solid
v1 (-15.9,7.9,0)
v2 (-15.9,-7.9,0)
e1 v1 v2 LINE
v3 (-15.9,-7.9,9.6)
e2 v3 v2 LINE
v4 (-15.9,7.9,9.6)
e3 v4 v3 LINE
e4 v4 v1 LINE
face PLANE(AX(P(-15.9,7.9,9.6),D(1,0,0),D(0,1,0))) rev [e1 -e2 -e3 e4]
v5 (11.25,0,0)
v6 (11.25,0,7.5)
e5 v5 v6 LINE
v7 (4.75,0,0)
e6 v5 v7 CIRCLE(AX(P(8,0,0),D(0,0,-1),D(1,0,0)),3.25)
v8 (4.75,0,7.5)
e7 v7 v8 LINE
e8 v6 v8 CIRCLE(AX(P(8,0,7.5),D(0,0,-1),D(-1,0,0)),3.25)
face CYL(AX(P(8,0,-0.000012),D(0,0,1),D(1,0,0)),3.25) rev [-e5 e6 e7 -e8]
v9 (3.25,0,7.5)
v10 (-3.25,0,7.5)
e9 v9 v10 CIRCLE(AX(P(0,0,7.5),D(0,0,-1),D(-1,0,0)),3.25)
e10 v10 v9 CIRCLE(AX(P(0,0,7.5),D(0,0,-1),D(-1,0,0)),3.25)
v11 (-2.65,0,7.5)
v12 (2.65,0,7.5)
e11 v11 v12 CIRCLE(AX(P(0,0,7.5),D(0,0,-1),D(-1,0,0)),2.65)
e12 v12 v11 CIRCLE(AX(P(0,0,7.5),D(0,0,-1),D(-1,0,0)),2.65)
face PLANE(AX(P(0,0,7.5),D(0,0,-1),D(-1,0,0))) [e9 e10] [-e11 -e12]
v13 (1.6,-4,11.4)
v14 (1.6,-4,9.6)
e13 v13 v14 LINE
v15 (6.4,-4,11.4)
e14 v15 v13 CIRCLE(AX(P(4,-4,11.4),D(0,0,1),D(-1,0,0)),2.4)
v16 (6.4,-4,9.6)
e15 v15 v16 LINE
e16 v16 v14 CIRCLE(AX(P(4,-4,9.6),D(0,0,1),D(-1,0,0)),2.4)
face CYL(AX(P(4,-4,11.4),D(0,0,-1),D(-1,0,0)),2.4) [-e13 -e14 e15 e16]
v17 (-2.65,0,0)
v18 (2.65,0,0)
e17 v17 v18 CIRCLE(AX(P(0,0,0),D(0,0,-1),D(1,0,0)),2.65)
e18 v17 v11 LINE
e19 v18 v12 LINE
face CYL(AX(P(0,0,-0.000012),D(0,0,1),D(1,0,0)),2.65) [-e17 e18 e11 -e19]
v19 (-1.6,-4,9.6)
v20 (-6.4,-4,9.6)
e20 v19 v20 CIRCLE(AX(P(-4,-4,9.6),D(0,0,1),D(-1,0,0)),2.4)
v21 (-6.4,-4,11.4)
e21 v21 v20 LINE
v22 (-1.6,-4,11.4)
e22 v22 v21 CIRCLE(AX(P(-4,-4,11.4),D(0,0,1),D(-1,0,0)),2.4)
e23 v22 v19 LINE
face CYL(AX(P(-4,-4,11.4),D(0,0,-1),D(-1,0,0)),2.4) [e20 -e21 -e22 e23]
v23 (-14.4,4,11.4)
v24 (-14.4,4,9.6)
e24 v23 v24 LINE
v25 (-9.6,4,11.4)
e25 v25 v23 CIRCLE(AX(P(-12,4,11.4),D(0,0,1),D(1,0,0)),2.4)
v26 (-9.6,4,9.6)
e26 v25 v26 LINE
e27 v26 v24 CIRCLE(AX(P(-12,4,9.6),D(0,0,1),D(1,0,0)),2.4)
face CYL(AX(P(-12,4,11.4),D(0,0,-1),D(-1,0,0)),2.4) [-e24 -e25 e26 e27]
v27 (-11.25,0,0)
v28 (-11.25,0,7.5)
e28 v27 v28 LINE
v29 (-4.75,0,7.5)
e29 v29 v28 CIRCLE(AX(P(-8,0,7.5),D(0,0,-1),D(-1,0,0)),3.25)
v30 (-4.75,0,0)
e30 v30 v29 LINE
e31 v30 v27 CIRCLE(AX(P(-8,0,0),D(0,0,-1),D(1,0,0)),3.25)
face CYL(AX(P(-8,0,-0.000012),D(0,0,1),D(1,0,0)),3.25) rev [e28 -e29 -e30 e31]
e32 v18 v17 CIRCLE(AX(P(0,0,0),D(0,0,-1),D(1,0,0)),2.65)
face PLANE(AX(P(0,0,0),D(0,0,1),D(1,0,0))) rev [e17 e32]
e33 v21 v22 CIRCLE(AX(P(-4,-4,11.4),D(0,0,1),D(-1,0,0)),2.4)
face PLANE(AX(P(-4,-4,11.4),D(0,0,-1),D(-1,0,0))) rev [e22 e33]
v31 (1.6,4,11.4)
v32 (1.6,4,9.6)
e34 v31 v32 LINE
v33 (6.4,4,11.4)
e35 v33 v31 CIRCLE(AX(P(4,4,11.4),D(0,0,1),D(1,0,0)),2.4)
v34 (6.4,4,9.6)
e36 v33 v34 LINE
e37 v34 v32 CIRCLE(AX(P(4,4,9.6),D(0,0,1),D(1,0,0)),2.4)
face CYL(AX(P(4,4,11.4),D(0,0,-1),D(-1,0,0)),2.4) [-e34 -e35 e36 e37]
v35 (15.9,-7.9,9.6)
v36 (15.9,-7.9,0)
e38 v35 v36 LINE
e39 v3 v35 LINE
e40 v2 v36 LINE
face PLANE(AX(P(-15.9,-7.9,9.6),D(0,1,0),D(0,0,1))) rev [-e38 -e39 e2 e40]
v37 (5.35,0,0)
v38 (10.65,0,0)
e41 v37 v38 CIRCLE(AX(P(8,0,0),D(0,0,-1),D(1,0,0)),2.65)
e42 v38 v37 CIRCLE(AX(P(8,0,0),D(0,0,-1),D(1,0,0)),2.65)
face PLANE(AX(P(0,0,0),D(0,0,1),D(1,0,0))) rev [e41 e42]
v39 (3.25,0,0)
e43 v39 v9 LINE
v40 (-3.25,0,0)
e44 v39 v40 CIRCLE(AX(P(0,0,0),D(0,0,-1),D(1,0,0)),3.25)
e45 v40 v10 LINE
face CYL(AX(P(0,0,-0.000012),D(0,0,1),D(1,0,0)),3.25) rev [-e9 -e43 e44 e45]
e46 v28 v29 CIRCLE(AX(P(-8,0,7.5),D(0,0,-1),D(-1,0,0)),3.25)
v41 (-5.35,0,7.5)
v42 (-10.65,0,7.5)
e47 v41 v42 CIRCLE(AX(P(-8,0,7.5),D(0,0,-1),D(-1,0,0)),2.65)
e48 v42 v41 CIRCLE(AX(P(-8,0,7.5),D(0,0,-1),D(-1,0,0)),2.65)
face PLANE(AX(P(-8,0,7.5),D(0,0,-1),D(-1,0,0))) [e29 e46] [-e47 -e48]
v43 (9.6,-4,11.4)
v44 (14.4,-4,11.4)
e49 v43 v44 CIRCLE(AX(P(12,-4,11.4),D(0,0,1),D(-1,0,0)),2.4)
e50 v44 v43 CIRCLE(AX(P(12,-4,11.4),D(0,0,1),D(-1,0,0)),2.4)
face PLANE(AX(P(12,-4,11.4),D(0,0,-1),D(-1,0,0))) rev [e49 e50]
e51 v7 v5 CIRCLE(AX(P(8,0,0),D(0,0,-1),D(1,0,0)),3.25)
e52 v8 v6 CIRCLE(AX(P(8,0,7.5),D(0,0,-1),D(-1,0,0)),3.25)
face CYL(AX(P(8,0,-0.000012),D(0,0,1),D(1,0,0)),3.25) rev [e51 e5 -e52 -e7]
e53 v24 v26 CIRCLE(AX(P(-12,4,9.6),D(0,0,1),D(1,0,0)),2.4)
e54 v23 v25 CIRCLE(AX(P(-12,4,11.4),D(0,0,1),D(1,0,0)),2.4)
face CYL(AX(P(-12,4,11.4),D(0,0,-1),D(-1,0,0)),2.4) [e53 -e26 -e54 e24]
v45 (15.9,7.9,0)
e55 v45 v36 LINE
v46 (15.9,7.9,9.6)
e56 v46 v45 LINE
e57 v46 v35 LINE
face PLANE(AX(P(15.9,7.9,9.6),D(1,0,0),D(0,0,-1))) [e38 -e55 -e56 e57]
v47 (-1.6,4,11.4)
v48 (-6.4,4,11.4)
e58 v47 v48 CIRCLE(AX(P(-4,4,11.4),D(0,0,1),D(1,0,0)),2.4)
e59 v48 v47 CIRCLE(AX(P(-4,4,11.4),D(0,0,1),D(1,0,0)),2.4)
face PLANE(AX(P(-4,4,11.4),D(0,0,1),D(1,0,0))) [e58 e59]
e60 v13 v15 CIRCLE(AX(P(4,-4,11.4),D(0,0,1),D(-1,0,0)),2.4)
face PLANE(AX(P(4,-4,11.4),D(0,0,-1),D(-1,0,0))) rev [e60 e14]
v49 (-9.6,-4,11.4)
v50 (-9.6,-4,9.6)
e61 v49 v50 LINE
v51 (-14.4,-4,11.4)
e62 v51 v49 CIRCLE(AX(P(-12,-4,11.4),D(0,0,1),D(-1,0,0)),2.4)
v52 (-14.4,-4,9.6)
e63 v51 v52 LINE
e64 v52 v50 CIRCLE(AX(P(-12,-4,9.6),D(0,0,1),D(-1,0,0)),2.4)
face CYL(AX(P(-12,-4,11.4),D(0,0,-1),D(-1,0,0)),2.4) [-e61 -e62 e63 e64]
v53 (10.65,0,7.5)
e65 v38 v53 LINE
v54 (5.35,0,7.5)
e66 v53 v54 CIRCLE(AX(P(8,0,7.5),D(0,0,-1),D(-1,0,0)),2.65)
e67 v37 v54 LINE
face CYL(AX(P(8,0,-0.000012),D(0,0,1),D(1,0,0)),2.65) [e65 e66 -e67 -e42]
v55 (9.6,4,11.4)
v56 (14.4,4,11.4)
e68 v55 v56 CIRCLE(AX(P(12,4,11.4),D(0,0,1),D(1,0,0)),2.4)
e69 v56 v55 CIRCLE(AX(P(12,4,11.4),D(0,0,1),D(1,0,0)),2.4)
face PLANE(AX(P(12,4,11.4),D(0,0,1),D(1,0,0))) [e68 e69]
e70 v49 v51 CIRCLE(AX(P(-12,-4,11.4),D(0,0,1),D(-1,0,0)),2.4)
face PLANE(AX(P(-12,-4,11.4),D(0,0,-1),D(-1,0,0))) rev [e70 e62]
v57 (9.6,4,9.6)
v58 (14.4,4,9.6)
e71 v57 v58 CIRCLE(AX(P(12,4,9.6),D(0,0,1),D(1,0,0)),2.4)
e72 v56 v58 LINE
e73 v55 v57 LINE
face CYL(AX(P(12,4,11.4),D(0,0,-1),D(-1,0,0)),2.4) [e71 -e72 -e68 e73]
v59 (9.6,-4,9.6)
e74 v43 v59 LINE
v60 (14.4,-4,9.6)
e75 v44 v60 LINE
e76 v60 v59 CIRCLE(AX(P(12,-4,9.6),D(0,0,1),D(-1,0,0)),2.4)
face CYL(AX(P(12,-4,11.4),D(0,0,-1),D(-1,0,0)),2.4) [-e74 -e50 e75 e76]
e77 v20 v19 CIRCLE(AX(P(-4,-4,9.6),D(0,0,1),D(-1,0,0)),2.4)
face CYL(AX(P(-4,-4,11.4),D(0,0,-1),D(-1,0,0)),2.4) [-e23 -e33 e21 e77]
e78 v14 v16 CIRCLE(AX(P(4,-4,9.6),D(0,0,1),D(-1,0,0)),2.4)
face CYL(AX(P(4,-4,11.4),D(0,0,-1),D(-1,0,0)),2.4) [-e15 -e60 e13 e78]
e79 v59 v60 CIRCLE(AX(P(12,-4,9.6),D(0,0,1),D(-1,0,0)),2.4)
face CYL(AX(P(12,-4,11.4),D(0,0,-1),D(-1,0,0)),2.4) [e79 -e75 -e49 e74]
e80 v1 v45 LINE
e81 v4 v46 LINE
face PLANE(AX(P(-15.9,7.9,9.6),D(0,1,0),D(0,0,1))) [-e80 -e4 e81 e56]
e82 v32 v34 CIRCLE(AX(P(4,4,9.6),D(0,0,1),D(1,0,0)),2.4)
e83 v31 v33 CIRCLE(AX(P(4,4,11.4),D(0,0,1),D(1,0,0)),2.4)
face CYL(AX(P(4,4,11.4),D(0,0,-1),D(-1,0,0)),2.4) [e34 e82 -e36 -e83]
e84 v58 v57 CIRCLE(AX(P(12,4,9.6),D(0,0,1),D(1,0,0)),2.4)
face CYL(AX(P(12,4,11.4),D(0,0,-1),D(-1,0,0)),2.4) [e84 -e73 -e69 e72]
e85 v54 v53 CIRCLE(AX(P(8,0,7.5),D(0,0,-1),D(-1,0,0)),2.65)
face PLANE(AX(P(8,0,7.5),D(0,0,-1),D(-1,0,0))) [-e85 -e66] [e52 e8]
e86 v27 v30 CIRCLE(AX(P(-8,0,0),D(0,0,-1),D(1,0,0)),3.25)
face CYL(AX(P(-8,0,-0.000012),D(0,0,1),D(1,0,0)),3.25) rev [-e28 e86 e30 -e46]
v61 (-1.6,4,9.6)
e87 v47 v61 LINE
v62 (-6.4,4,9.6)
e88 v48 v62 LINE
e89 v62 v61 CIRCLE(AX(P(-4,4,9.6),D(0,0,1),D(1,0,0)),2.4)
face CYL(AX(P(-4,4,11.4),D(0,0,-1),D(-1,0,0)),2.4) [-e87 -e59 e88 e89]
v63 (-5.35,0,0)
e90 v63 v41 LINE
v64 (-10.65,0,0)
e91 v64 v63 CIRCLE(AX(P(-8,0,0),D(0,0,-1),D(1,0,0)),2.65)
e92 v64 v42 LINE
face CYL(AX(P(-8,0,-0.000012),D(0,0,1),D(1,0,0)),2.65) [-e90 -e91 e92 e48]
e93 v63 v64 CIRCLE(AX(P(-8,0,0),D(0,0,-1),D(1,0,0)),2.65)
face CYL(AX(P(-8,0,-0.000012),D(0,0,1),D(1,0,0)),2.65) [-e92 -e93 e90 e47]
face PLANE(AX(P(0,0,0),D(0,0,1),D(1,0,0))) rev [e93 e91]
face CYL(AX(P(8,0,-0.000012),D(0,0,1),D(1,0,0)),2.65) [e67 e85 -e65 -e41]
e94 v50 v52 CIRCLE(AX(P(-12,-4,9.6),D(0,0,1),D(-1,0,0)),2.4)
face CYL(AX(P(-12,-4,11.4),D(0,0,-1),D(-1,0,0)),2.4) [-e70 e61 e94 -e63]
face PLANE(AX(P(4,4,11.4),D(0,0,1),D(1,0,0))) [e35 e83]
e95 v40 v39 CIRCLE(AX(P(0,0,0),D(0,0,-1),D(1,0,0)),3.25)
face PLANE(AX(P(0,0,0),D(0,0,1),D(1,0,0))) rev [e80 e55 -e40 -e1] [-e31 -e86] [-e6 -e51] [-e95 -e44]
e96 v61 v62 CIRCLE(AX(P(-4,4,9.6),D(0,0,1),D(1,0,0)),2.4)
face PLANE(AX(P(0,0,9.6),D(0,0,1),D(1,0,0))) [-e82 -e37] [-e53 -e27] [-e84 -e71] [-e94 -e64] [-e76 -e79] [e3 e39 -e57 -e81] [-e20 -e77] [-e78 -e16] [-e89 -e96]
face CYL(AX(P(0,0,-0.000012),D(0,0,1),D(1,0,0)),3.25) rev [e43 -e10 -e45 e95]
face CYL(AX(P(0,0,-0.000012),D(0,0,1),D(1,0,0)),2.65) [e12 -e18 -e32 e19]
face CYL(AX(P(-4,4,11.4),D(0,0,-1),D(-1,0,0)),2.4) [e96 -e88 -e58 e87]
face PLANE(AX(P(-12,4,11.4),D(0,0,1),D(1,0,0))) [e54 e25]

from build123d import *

# Parameters (mm, degrees)
BRICK_BODY_PROFILE_W         = 31.8
BRICK_BODY_PROFILE_H         = 15.8
BRICK_BODY_DEPTH             = 9.6
STUDS_PROFILE_2X4_4_8_R      = 2.4
STUDS_8X_4_8_DEPTH           = 1.8
UNDERSIDE_CAVITY_DEPTH       = 22.099289088
UNDERSIDE_CAVITY_DEPTH_BACK  = 7.5
UNDERSIDE_CAVITY_PROFILE_R   = 3.25
UNDERSIDE_CAVITY_PROFILE_R_2 = 2.65


with BuildPart() as part:
    # Brick Body Profile → Brick Body (new body)
    with BuildSketch(Plane.XY):
        Rectangle(BRICK_BODY_PROFILE_W, BRICK_BODY_PROFILE_H)
    extrude(amount=BRICK_BODY_DEPTH)

    # Studs Profile 2x4 Ø4.8 → Studs 8xØ4.8 (add)
    with BuildSketch(Plane.XY.offset(9.6)):
        with Locations((-12, 4)):
            Circle(STUDS_PROFILE_2X4_4_8_R)
        with Locations((-4, 4)):
            Circle(STUDS_PROFILE_2X4_4_8_R)
        with Locations((4, 4)):
            Circle(STUDS_PROFILE_2X4_4_8_R)
        with Locations((12, 4)):
            Circle(STUDS_PROFILE_2X4_4_8_R)
        with Locations(Location((12, -4, 0), (0, 0, 180))):
            Circle(STUDS_PROFILE_2X4_4_8_R)
        with Locations(Location((4, -4, 0), (0, 0, 180))):
            Circle(STUDS_PROFILE_2X4_4_8_R)
        with Locations(Location((-4, -4, 0), (0, 0, 180))):
            Circle(STUDS_PROFILE_2X4_4_8_R)
        with Locations(Location((-12, -4, 0), (0, 0, 180))):
            Circle(STUDS_PROFILE_2X4_4_8_R)
    extrude(amount=STUDS_8X_4_8_DEPTH)

    # Underside Cavity Profile → Underside Cavity (cut, two sides: drawn at the far end of the back side and taken through both)
    # profile 1 of 3: a face of its own
    with BuildSketch(Plane(origin=(0, 0, 0), x_dir=(-1, 0, 0), z_dir=(0, 0, -1)).offset(-UNDERSIDE_CAVITY_DEPTH_BACK)):
        with Locations(Location((-8, 0, 0), (0, 0, 180))):
            Circle(UNDERSIDE_CAVITY_PROFILE_R)
        with Locations(Location((-8, 0, 0), (0, 0, 180))):
            Circle(UNDERSIDE_CAVITY_PROFILE_R_2, mode=Mode.SUBTRACT)
    # profile 2 of 3: a face of its own
    with BuildSketch(Plane(origin=(0, 0, 0), x_dir=(-1, 0, 0), z_dir=(0, 0, -1)).offset(-UNDERSIDE_CAVITY_DEPTH_BACK)):
        with Locations(Location((0, 0, 0), (0, 0, 180))):
            Circle(UNDERSIDE_CAVITY_PROFILE_R)
        with Locations(Location((0, 0, 0), (0, 0, 180))):
            Circle(UNDERSIDE_CAVITY_PROFILE_R_2, mode=Mode.SUBTRACT)
    # profile 3 of 3: a face of its own
    with BuildSketch(Plane(origin=(0, 0, 0), x_dir=(-1, 0, 0), z_dir=(0, 0, -1)).offset(-UNDERSIDE_CAVITY_DEPTH_BACK)):
        with Locations(Location((8, 0, 0), (0, 0, 180))):
            Circle(UNDERSIDE_CAVITY_PROFILE_R)
        with Locations(Location((8, 0, 0), (0, 0, 180))):
            Circle(UNDERSIDE_CAVITY_PROFILE_R_2, mode=Mode.SUBTRACT)
    extrude(amount=UNDERSIDE_CAVITY_DEPTH + UNDERSIDE_CAVITY_DEPTH_BACK, mode=Mode.SUBTRACT)


solid = part.part
